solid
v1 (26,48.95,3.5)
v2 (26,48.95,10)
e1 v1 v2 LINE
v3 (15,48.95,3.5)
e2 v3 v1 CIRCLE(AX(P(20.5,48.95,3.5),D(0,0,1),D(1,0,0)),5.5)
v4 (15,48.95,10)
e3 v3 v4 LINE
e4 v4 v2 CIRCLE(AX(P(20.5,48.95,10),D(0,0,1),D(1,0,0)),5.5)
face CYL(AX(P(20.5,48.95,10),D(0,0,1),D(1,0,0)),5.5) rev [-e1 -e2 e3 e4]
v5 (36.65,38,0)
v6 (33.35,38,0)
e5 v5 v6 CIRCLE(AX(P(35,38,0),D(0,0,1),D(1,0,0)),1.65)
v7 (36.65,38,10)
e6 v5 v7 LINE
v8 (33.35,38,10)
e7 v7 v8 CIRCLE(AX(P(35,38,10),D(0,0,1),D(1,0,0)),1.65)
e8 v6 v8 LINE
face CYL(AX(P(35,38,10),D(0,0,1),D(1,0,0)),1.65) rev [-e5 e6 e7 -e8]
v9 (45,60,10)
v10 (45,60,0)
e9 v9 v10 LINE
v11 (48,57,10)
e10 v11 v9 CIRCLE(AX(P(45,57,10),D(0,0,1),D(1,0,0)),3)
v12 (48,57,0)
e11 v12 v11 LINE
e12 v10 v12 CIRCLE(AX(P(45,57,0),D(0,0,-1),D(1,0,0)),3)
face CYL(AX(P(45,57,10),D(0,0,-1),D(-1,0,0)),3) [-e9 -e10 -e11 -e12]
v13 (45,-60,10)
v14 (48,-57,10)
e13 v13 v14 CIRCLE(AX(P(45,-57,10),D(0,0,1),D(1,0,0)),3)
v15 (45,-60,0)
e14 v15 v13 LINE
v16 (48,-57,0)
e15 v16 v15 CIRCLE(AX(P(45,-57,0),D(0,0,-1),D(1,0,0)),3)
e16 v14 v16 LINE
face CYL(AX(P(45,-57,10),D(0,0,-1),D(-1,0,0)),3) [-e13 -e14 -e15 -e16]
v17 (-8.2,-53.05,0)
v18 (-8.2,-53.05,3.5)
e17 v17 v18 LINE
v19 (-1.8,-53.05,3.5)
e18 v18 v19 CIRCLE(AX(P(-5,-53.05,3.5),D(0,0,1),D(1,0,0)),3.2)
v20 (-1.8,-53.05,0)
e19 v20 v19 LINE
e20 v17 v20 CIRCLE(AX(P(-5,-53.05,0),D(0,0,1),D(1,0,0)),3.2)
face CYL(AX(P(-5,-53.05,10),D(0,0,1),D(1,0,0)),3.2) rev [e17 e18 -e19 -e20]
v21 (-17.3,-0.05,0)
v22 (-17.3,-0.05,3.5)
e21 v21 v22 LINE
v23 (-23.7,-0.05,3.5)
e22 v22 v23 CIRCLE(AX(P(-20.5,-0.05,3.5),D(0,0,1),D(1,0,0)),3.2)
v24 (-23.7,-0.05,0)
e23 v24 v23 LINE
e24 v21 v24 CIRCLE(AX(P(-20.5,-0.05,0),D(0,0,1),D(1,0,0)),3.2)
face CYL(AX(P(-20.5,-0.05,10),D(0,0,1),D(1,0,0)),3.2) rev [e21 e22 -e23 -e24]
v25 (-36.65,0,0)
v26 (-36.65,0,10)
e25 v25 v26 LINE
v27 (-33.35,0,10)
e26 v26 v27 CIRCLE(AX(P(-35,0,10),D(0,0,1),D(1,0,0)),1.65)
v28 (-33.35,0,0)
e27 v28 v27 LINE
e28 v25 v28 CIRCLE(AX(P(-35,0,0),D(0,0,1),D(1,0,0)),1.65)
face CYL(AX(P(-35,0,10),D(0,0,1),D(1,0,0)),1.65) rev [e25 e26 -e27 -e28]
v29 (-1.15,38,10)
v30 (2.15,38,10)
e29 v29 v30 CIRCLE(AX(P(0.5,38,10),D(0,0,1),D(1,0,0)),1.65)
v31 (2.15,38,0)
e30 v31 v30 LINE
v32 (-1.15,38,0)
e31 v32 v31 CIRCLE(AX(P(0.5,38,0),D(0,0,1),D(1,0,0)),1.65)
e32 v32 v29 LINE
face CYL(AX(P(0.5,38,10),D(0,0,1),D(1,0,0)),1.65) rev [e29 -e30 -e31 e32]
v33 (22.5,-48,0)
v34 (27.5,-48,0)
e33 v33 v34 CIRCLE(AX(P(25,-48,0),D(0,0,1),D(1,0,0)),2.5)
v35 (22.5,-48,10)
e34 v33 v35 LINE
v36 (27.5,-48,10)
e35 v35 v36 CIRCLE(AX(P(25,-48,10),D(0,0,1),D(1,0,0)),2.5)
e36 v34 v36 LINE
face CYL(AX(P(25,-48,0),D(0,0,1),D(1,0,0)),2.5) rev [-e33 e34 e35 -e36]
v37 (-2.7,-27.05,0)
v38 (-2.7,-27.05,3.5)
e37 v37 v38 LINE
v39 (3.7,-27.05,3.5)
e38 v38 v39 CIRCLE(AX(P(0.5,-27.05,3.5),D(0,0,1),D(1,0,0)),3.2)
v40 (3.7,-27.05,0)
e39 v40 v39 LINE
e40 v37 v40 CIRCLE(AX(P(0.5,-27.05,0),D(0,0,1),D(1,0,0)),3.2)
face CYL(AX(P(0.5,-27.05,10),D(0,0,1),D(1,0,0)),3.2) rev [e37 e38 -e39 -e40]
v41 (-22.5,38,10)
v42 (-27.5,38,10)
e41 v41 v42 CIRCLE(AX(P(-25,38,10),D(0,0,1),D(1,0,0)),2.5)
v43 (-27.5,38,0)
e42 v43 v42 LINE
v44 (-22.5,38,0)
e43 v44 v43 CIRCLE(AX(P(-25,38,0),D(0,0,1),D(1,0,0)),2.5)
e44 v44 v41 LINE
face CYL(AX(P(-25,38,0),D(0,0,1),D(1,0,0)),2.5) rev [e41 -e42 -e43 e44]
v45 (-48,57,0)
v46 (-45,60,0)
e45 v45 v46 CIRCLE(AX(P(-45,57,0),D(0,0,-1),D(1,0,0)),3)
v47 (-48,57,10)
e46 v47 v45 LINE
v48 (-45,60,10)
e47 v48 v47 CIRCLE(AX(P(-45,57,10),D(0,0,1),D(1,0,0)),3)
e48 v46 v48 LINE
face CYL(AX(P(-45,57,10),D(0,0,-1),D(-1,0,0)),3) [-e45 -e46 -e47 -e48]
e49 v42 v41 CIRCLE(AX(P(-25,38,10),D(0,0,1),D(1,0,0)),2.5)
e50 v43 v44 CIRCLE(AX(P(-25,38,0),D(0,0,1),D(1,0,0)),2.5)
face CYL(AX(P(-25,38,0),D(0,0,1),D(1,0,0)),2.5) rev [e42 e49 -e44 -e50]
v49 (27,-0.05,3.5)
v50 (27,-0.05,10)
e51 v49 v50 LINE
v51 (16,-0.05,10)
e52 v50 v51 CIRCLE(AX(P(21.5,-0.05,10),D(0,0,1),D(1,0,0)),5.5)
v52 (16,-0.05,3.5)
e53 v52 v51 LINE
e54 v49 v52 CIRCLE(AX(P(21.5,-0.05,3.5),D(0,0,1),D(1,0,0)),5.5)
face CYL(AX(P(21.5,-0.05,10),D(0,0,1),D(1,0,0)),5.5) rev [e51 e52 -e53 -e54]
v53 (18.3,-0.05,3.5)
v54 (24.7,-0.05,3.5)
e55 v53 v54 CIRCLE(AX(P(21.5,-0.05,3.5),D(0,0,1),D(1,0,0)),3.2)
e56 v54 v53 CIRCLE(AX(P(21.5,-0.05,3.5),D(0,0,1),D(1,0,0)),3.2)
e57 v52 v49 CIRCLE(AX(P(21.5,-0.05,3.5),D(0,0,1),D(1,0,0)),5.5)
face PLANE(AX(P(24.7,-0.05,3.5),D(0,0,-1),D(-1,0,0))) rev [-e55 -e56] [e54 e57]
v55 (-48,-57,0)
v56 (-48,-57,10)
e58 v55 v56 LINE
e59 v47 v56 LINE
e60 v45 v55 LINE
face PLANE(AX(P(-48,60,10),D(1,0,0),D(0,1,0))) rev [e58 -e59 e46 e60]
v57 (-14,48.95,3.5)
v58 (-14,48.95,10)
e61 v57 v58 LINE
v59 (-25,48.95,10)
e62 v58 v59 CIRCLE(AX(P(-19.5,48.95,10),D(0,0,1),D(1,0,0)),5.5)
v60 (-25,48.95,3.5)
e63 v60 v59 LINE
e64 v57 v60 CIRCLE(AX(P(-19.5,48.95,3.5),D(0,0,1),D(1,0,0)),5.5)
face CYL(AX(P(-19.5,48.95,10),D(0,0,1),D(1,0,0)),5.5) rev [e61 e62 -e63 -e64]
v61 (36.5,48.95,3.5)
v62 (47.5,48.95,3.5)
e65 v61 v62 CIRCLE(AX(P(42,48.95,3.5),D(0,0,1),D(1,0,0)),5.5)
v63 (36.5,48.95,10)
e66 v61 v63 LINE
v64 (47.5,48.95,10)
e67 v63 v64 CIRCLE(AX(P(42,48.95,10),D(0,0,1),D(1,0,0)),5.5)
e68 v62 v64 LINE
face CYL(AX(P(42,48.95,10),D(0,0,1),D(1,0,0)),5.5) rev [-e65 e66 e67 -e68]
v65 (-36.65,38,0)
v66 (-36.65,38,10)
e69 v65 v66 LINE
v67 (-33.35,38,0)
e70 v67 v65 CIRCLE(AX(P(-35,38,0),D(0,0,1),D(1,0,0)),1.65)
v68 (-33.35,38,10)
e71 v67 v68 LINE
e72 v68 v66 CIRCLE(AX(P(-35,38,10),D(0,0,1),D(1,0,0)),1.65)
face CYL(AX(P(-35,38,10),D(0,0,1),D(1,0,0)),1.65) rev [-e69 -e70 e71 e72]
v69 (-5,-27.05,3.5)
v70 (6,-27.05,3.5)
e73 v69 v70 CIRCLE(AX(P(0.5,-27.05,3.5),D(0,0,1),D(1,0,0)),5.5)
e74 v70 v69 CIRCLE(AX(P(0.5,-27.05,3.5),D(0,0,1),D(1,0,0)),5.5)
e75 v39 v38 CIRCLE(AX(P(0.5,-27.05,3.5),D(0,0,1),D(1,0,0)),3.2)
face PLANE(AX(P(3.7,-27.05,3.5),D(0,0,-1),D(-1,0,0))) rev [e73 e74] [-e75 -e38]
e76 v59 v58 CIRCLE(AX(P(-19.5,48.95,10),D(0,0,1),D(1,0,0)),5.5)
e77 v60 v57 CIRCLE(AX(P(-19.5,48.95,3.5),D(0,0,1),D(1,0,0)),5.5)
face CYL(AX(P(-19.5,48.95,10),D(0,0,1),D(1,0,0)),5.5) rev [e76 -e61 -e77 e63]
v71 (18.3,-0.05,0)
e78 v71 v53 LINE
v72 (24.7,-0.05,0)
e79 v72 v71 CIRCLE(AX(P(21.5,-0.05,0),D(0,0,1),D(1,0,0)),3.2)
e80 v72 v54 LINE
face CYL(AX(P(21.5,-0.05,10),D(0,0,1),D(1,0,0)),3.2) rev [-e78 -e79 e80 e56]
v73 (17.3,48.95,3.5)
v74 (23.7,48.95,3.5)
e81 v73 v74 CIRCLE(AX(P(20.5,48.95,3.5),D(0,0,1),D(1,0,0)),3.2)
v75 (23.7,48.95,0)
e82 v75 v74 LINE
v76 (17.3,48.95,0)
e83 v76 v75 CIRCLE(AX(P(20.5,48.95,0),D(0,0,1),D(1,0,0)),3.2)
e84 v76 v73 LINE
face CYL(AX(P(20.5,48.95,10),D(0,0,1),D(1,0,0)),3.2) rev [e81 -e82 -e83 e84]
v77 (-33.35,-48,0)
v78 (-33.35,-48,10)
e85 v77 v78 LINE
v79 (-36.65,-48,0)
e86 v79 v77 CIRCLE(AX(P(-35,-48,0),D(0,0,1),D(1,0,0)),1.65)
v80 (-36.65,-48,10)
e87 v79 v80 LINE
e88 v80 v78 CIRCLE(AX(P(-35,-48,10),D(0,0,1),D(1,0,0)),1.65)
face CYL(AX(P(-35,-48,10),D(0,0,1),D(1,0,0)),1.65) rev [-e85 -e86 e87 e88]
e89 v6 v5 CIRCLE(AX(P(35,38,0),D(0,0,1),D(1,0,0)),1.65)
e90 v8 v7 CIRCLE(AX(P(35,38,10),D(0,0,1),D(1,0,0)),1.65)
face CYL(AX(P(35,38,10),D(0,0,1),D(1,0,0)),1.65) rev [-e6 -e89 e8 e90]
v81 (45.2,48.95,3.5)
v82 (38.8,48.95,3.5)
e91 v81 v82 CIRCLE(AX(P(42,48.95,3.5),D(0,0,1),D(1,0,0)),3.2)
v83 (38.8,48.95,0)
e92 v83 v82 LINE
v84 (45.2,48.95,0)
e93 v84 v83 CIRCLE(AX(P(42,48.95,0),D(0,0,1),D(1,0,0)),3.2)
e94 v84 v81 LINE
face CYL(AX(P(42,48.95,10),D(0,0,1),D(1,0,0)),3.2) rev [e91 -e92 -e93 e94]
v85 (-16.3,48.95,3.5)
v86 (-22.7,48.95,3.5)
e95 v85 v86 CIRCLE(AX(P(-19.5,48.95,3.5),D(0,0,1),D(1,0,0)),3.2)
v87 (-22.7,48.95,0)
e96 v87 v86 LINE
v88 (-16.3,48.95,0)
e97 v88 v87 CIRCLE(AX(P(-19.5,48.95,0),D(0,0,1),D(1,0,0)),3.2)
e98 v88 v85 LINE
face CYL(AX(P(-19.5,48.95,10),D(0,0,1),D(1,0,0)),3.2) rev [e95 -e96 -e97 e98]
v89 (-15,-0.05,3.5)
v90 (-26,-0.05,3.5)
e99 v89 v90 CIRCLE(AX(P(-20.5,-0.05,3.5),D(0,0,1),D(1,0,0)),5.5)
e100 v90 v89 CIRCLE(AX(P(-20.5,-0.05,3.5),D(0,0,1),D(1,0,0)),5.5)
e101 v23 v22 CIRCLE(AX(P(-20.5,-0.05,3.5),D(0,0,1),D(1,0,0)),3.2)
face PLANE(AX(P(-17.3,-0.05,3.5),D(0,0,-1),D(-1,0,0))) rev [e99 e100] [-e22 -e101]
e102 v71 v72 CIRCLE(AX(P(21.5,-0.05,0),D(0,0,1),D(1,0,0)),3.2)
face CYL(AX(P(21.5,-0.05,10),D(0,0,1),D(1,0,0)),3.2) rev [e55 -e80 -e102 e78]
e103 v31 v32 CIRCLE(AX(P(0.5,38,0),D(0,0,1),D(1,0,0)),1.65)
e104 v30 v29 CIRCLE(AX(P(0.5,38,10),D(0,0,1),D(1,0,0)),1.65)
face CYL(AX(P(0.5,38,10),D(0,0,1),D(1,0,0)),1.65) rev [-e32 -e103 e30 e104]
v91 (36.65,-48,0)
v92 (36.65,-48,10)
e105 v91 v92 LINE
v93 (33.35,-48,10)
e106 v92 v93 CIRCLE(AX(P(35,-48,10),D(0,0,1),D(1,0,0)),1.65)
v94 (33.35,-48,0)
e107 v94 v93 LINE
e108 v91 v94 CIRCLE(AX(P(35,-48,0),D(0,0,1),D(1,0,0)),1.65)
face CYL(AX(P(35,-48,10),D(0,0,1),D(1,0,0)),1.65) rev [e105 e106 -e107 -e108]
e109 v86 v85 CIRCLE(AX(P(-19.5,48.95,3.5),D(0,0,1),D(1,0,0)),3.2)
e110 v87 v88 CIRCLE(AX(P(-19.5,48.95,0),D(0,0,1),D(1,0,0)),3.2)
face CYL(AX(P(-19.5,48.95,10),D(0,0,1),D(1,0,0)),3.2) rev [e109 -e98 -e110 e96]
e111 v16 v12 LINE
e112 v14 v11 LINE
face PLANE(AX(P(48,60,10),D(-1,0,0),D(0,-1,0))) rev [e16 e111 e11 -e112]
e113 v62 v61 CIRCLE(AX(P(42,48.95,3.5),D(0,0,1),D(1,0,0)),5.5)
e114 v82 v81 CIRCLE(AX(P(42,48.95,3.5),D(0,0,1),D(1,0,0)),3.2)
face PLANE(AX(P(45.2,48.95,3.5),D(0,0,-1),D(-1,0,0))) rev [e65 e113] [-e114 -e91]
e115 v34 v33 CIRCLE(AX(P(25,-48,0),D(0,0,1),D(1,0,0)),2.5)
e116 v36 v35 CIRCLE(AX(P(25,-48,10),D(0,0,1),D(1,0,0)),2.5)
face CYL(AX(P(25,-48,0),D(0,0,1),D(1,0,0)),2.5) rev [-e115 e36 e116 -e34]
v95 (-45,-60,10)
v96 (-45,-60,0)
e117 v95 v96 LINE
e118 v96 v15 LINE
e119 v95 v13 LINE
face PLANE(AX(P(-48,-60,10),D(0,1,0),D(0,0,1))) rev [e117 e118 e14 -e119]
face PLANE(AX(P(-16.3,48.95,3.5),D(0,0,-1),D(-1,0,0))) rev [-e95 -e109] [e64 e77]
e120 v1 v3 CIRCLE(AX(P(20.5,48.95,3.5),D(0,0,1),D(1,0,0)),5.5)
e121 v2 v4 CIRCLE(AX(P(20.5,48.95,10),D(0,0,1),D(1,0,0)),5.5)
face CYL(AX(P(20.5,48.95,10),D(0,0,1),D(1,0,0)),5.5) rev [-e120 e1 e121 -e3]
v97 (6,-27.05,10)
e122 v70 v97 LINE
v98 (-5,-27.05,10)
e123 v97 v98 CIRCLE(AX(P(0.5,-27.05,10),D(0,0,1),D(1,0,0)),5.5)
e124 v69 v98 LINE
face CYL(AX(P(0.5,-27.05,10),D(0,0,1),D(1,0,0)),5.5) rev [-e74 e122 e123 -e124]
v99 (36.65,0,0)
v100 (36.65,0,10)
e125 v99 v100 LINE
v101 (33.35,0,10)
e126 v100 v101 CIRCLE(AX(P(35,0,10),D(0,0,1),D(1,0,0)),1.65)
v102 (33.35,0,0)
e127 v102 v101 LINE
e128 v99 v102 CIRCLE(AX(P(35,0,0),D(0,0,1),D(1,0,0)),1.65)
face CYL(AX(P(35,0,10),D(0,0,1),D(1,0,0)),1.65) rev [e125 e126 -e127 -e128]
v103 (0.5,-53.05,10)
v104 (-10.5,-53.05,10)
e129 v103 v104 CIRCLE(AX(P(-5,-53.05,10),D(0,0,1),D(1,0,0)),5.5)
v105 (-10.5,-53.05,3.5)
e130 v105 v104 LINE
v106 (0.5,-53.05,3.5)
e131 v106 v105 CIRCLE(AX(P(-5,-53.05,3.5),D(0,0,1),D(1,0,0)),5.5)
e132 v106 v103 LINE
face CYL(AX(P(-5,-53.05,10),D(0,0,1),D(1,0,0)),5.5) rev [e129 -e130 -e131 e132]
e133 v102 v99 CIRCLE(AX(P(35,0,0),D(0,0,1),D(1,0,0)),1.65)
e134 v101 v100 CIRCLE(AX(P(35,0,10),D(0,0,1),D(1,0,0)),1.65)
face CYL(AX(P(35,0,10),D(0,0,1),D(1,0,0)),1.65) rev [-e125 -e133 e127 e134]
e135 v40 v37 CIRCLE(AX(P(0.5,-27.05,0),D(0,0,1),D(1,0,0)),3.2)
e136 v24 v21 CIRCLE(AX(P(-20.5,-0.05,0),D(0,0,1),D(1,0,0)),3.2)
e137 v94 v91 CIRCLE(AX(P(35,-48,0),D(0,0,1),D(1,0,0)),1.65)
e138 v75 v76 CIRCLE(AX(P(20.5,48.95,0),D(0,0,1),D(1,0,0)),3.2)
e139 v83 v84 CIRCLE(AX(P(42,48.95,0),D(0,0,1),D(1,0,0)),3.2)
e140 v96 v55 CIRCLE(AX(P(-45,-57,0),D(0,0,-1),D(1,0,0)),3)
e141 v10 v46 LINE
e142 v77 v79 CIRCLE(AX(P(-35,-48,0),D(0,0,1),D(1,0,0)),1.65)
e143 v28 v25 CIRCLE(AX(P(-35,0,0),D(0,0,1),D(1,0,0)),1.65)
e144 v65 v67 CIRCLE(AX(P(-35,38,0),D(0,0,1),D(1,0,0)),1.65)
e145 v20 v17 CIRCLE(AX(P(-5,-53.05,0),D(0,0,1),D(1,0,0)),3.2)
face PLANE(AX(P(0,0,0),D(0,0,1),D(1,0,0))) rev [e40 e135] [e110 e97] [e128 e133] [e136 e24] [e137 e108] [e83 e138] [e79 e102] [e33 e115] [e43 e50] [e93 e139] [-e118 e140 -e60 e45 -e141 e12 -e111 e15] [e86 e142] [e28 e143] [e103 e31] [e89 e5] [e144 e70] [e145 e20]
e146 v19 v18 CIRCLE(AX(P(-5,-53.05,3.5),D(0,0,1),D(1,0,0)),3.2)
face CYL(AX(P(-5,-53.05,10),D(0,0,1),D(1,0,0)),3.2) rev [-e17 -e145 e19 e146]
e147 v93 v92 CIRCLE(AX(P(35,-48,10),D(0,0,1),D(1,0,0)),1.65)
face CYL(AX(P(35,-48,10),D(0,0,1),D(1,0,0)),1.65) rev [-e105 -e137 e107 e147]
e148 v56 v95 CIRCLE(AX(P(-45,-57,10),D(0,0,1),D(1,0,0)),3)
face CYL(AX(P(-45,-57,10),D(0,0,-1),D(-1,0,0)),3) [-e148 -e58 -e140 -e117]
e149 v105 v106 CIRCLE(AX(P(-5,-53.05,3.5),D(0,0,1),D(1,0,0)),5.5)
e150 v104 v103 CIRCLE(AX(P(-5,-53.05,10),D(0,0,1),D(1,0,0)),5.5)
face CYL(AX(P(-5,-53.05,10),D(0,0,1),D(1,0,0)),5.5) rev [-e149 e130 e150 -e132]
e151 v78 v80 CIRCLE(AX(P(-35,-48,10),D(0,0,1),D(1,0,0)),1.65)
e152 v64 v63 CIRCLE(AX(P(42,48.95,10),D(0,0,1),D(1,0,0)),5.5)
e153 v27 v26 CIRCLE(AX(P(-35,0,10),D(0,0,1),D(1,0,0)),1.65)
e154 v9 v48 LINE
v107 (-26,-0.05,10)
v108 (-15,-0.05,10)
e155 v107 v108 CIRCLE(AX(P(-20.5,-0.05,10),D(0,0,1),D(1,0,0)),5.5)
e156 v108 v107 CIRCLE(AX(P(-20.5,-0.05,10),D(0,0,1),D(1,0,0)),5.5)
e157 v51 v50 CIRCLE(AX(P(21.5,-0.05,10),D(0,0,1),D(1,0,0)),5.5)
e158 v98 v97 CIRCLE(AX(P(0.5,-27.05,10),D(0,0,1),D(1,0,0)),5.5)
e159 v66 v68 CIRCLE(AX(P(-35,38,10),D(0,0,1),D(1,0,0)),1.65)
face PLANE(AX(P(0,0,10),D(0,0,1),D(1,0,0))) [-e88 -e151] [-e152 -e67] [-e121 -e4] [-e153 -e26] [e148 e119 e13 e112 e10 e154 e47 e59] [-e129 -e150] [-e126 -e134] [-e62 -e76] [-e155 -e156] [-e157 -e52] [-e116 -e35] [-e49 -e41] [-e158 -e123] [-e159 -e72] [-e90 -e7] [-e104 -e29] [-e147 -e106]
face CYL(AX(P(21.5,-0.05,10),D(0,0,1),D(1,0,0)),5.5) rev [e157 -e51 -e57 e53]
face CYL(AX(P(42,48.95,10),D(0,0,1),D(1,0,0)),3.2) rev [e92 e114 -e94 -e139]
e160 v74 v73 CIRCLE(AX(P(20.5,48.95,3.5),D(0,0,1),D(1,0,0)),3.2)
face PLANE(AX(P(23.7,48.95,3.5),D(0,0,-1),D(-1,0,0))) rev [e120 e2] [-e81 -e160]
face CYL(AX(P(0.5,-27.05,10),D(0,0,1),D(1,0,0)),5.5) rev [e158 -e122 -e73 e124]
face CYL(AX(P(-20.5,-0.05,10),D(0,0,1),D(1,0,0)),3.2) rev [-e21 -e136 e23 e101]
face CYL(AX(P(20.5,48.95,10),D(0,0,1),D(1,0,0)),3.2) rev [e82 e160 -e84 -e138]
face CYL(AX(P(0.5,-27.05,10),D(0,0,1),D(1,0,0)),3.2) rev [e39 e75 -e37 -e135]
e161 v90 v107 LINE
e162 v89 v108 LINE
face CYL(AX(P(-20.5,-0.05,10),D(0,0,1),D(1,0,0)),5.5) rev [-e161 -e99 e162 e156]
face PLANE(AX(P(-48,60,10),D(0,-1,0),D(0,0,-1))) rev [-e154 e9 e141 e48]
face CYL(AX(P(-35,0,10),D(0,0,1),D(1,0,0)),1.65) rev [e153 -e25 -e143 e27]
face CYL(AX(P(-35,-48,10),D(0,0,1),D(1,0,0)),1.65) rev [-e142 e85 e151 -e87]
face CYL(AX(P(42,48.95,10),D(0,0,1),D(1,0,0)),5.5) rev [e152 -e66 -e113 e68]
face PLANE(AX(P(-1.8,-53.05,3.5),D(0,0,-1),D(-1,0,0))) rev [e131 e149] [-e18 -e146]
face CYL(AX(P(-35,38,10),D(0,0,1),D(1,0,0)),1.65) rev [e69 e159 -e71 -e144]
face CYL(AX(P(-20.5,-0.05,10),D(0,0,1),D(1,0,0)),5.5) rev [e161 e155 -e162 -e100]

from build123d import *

# Parameters (mm, degrees)
SKETCH_1_W                = 96
SKETCH_1_H                = 120
EXTRUDE_1_DEPTH           = 10
HOLE_WIZARD_2_D           = 6.4
HOLE_WIZARD_2_CBORE_D     = 11
HOLE_WIZARD_2_CBORE_DEPTH = 6.5
FILLET_1_R                = 3
HOLE_WIZARD_M4_1_D        = 3.3
SKETCH_7_R                = 2.5
CUT_EXTRUDE_1_DEPTH       = 10


with BuildPart() as part:
    # 草图1 → 凸台-拉伸1 (new body)
    with BuildSketch(Plane.XY):
        Rectangle(SKETCH_1_W, SKETCH_1_H)
    extrude(amount=EXTRUDE_1_DEPTH)

    # 打孔尺寸(%根据)内六角圆柱头螺钉的类型2 (through all)
    with Locations(Plane.XY.offset(10)):
        with Locations((-19.5, 48.95), (20.5, 48.95), (42, 48.95), (21.5, -0.05), (-20.5, -0.05), (0.5, -27.05), (-5, -53.05)):
            CounterBoreHole(HOLE_WIZARD_2_D / 2, HOLE_WIZARD_2_CBORE_D / 2, HOLE_WIZARD_2_CBORE_DEPTH)

    # 圆角1
    fillet_1_edges = [part.edges().sort_by_distance(p)[0] for p in [
        (48, -60, 5),
        (-48, -60, 5),
        (-48, 60, 5),
        (48, 60, 5),
    ]]
    fillet(fillet_1_edges, radius=FILLET_1_R)

    # M4 螺纹孔1 (through all)
    with Locations(Plane.XY.offset(10)):
        with Locations((-35, -48), (-35, 0), (35, 0), (35, -48), (-35, 38), (35, 38), (0.5, 38)):
            Hole(HOLE_WIZARD_M4_1_D / 2)

    # 草图7 → 切除-拉伸1 (cut)
    with BuildSketch(Plane.XY.offset(10)):
        with Locations((-25, 38)):
            Circle(SKETCH_7_R)
        with Locations((25, -48)):
            Circle(SKETCH_7_R)
    extrude(amount=-CUT_EXTRUDE_1_DEPTH, mode=Mode.SUBTRACT)


solid = part.part
